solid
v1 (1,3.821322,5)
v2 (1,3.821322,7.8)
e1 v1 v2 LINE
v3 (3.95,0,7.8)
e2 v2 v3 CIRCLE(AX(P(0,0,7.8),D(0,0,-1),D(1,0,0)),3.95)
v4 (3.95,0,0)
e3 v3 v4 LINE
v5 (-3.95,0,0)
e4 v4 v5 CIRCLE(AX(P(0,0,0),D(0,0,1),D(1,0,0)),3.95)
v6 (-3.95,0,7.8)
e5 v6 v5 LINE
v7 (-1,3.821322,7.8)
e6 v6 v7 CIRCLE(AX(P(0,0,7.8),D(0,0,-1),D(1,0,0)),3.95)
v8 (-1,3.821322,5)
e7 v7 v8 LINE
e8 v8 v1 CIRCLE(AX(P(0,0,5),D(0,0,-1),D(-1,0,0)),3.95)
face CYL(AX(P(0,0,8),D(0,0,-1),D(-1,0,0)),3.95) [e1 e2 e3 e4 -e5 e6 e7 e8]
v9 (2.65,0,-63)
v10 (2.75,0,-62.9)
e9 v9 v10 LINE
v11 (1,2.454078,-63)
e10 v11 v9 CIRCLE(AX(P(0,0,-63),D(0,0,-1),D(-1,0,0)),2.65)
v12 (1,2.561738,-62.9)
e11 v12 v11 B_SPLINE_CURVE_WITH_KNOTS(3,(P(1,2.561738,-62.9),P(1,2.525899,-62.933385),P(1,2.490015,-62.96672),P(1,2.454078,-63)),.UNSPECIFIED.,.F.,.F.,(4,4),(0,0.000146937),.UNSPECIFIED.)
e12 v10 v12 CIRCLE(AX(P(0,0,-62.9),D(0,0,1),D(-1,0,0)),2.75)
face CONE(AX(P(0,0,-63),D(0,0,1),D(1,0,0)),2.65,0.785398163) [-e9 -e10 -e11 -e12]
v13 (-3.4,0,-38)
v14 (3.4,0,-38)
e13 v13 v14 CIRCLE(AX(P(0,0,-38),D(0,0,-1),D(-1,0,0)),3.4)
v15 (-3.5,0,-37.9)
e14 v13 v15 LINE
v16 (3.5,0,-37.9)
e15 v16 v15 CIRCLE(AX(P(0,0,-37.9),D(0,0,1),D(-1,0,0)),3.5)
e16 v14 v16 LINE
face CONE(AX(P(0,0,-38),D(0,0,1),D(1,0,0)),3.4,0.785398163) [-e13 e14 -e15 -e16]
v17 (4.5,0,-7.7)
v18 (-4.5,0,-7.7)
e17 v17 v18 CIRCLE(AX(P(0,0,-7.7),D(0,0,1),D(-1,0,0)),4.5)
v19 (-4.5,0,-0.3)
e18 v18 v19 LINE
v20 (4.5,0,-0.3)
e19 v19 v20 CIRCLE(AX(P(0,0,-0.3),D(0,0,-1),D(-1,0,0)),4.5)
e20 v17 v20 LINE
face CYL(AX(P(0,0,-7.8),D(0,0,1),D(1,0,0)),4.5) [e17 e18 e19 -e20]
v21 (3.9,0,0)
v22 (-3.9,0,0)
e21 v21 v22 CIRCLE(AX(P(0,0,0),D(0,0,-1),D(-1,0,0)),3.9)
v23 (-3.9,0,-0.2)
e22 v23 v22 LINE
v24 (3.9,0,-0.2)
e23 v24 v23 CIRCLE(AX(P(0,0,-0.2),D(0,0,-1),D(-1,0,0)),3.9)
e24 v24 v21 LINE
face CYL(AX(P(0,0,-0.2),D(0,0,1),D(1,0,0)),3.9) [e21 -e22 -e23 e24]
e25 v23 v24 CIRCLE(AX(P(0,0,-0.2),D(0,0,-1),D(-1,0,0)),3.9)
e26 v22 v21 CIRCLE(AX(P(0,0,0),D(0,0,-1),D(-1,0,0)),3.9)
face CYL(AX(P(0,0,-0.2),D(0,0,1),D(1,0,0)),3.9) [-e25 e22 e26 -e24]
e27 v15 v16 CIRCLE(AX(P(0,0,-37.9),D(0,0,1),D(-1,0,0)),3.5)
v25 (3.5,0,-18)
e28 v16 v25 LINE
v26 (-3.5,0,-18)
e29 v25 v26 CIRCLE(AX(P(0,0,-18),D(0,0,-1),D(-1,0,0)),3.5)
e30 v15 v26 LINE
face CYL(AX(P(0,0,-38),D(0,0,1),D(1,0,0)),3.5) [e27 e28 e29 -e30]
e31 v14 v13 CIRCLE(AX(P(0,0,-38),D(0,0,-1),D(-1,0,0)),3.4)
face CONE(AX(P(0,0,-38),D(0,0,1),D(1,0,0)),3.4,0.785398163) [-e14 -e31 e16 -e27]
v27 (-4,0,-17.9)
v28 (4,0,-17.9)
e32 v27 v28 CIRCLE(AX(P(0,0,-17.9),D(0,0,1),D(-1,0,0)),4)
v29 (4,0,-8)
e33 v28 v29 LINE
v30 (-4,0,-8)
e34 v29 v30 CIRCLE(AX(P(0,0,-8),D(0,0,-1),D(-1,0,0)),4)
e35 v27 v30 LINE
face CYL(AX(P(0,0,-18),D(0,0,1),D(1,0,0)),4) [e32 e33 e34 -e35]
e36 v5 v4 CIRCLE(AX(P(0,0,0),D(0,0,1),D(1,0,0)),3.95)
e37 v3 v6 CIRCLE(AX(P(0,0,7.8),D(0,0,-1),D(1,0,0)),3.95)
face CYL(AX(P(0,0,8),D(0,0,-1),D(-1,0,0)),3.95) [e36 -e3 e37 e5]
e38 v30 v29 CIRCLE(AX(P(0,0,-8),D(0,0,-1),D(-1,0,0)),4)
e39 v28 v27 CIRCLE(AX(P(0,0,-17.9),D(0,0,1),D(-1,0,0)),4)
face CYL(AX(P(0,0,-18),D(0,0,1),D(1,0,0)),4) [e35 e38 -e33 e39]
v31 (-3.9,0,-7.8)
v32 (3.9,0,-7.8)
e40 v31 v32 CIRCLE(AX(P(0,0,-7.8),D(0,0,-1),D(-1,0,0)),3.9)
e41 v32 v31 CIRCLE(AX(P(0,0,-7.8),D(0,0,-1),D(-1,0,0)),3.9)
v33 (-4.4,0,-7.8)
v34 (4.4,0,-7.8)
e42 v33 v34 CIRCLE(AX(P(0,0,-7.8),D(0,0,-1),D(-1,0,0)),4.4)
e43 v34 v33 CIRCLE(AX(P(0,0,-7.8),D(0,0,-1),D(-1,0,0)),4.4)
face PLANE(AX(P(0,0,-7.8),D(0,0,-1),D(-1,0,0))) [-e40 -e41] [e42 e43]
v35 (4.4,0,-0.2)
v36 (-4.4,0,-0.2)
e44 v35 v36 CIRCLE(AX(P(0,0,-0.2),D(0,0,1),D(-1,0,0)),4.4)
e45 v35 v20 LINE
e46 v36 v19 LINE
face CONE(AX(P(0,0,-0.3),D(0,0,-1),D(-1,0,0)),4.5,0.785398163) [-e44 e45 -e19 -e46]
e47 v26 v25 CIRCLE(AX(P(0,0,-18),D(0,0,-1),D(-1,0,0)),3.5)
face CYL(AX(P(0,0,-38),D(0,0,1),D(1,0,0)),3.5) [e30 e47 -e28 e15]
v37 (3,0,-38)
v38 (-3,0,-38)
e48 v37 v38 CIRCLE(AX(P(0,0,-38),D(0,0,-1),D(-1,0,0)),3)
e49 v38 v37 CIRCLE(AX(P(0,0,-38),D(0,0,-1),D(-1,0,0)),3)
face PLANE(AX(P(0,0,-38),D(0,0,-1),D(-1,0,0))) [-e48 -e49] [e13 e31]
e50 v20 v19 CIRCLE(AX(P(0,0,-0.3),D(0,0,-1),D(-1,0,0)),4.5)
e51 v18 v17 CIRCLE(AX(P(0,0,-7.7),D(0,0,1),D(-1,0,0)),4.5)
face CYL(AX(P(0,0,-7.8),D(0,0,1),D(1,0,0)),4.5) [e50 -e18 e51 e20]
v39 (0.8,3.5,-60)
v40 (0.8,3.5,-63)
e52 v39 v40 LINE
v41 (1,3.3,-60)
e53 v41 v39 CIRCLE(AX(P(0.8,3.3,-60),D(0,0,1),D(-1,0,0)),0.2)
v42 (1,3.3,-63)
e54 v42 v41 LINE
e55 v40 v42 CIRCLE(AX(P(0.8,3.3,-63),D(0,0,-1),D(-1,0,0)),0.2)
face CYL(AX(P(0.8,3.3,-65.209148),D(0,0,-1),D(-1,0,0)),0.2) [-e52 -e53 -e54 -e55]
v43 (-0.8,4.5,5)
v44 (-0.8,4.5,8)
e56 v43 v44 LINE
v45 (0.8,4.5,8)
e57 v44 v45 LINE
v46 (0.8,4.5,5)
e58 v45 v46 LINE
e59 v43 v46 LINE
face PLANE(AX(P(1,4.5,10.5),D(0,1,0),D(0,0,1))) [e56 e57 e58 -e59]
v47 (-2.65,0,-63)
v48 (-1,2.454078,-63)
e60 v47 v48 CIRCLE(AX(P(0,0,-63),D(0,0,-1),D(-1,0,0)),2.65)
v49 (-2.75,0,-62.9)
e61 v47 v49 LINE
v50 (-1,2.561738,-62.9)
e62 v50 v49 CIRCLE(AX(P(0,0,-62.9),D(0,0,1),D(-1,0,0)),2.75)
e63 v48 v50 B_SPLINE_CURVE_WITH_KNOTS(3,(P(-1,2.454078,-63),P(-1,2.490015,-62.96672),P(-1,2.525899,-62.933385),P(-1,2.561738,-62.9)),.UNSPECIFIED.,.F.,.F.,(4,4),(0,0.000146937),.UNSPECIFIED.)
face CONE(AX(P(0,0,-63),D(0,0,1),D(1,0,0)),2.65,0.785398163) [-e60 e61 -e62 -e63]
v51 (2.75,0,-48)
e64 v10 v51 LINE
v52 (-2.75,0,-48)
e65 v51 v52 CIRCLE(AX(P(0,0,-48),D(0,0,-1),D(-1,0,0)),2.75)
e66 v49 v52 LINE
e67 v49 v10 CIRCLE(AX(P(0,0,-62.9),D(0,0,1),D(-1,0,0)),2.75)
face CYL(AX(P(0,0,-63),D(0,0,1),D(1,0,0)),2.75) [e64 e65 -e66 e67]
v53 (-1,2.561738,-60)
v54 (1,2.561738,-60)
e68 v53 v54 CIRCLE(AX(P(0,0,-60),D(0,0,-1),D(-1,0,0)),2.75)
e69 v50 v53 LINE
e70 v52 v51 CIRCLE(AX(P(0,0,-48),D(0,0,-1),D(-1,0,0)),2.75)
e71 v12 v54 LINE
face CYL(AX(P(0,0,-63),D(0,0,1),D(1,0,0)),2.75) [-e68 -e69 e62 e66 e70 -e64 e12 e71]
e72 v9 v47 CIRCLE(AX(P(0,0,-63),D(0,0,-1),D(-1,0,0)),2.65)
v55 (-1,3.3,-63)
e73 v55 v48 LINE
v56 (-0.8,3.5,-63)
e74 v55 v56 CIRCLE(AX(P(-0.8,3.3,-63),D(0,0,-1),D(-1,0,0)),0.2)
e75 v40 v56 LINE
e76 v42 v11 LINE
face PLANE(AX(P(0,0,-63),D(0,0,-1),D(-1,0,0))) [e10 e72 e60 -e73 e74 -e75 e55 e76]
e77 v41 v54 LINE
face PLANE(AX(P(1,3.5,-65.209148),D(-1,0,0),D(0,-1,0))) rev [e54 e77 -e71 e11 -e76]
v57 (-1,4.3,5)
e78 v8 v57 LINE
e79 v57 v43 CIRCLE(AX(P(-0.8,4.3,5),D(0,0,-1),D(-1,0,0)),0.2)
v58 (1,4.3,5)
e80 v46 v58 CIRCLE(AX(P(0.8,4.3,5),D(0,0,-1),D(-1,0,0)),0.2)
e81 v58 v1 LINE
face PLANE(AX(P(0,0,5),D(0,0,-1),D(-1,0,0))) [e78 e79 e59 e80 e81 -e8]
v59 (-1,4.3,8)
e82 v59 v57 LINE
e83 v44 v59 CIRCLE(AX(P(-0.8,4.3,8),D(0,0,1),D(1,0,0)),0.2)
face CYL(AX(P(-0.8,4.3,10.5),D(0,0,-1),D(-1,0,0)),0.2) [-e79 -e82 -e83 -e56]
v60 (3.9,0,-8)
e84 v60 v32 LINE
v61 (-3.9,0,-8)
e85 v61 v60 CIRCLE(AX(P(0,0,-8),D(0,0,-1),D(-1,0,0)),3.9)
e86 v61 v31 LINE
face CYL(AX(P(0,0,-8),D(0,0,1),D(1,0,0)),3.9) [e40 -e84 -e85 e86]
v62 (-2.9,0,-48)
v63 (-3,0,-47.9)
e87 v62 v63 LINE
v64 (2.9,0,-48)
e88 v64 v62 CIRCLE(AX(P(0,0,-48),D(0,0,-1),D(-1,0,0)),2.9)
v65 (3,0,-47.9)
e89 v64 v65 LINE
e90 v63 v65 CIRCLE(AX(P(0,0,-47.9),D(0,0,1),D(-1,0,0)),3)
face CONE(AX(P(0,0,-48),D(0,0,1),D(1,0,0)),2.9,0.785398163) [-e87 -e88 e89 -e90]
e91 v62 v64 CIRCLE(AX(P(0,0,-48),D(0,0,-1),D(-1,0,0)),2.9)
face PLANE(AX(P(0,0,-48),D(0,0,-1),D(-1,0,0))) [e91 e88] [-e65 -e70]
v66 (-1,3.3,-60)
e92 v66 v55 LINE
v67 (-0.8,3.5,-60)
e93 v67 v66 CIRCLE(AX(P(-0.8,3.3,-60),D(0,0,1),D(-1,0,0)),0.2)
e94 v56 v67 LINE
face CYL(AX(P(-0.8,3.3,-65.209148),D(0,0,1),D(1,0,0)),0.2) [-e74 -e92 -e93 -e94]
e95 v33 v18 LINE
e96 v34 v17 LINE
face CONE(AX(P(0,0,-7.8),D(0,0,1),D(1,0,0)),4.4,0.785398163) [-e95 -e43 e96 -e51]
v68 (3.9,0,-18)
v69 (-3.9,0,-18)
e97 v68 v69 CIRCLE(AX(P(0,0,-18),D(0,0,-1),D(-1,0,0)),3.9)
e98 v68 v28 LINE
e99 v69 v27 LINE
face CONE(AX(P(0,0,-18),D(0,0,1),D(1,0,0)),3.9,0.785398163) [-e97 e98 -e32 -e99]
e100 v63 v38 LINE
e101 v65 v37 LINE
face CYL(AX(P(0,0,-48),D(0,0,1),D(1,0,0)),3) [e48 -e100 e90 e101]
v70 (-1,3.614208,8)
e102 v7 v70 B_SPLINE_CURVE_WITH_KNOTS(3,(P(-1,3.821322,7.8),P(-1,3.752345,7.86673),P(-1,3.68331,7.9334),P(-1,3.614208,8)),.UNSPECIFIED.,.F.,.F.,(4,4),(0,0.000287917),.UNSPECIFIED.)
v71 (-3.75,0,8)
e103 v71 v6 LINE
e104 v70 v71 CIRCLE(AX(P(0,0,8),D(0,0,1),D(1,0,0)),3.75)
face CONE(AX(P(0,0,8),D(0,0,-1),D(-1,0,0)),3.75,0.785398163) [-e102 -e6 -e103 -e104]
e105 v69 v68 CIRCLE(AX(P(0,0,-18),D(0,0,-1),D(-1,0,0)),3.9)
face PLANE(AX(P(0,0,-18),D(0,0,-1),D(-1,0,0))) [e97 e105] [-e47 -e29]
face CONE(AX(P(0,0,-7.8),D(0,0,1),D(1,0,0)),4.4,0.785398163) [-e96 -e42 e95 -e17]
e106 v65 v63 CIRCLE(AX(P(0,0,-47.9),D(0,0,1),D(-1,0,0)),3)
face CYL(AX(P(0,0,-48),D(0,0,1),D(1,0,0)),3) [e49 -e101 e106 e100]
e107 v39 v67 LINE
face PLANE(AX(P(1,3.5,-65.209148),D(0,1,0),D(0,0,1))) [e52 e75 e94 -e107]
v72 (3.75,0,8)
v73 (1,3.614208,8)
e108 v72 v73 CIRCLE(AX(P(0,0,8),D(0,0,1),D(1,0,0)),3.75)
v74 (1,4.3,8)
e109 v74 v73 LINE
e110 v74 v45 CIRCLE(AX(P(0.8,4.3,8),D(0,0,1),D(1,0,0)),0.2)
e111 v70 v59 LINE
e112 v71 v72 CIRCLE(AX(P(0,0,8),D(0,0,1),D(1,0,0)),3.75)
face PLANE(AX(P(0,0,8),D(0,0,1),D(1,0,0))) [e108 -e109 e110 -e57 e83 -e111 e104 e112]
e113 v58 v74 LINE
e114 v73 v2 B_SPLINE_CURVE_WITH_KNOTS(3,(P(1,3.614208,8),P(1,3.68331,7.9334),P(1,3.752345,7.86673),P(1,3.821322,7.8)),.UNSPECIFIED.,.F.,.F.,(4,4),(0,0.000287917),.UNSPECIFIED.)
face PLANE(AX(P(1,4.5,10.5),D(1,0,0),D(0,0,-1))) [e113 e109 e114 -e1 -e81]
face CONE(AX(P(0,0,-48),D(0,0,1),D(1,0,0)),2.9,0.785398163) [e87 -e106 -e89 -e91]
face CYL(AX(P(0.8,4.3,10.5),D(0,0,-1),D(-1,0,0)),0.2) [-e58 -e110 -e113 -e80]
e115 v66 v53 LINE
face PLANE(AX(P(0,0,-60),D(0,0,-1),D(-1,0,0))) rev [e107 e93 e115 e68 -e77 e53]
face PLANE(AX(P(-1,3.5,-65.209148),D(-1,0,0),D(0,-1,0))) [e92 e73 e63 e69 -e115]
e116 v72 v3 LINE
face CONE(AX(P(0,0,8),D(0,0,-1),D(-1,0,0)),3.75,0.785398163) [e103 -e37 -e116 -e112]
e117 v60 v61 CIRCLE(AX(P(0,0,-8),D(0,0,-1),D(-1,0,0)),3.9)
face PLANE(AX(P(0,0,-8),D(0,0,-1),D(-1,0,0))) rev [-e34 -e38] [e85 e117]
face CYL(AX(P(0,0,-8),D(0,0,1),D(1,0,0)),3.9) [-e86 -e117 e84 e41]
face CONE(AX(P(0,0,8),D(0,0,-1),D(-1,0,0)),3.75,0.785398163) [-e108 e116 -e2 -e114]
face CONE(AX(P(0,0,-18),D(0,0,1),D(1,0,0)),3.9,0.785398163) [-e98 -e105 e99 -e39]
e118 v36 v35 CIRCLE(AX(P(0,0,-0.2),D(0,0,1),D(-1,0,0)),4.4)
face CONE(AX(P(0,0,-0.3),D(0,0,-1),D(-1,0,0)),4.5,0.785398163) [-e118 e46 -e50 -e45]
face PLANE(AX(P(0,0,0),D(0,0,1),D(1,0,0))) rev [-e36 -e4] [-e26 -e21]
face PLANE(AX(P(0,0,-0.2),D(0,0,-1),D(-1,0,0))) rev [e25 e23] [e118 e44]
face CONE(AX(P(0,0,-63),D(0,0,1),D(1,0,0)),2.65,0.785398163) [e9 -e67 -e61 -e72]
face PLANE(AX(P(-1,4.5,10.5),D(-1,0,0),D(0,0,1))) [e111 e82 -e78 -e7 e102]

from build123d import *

# Parameters (mm, degrees)
SKETCH1_R            = 3.95
BOSS_EXTRUDE1_DEPTH  = 8
SKETCH2_W            = 2
SKETCH2_H            = 1.5
BOSS_EXTRUDE2_DEPTH  = 3
FILLET1_R            = 0.2
SKETCH3_R            = 3.9
BOSS_EXTRUDE3_DEPTH  = 0.2
SKETCH4_R            = 4.5
BOSS_EXTRUDE4_DEPTH  = 7.6
SKETCH6_R            = 3.9
BOSS_EXTRUDE5_DEPTH  = 0.2
CHAMFER2_SIZE        = 0.2
SKETCH7_R            = 4
BOSS_EXTRUDE8_DEPTH  = 10
SKETCH9_R            = 3.5
BOSS_EXTRUDE9_DEPTH  = 20
SKETCH10_R           = 3
BOSS_EXTRUDE10_DEPTH = 10
SKETCH13_R           = 2.75
BOSS_EXTRUDE11_DEPTH = 15
BOSS_EXTRUDE13_DEPTH = 3
FILLET2_R            = 0.2
CHAMFER5_SIZE        = 0.1


with BuildPart() as part:
    # Sketch1 → Boss-Extrude1 (new body)
    with BuildSketch(Plane.XY):
        Circle(SKETCH1_R)
    extrude(amount=BOSS_EXTRUDE1_DEPTH)

    # Sketch2 → Boss-Extrude2 (add)
    with BuildSketch(Plane(origin=(0, 0, 5), x_dir=(-1, 0, 0), z_dir=(0, 0, -1))):
        with Locations((0, 3.75)):
            Rectangle(SKETCH2_W, SKETCH2_H)
    extrude(amount=-BOSS_EXTRUDE2_DEPTH)

    # Fillet1
    fillet1_edges = [part.edges().sort_by_distance(p)[0] for p in [
        (-1, 4.5, 6.5),
        (1, 4.5, 6.5),
    ]]
    fillet(fillet1_edges, radius=FILLET1_R)

    # Sketch3 → Boss-Extrude3 (add)
    with BuildSketch(Plane(origin=(0, 0, 0), x_dir=(-1, 0, 0), z_dir=(0, 0, -1))):
        Circle(SKETCH3_R)
    extrude(amount=BOSS_EXTRUDE3_DEPTH)

    # Sketch4 → Boss-Extrude4 (add)
    with BuildSketch(Plane(origin=(0, 0, -0.2), x_dir=(-1, 0, 0), z_dir=(0, 0, -1))):
        with Locations(Location((0, 0, 0), (0, 0, 180))):
            Circle(SKETCH4_R)
    extrude(amount=BOSS_EXTRUDE4_DEPTH)

    # Sketch6 → Boss-Extrude5 (add)
    with BuildSketch(Plane(origin=(0, 0, -7.8), x_dir=(-1, 0, 0), z_dir=(0, 0, -1))):
        Circle(SKETCH6_R)
    extrude(amount=BOSS_EXTRUDE5_DEPTH)

    # Chamfer2
    chamfer2_edges = [part.edges().sort_by_distance(p)[0] for p in [
        (-2.413762623, -3.126699538, 8),
    ]]
    chamfer(chamfer2_edges, length=CHAMFER2_SIZE)

    # Sketch7 → Boss-Extrude8 (add)
    with BuildSketch(Plane(origin=(0, 0, -8), x_dir=(-1, 0, 0), z_dir=(0, 0, -1))):
        Circle(SKETCH7_R)
    extrude(amount=BOSS_EXTRUDE8_DEPTH)

    # Sketch9 → Boss-Extrude9 (add)
    with BuildSketch(Plane(origin=(0, 0, -18), x_dir=(-1, 0, 0), z_dir=(0, 0, -1))):
        Circle(SKETCH9_R)
    extrude(amount=BOSS_EXTRUDE9_DEPTH)

    # Sketch10 → Boss-Extrude10 (add)
    with BuildSketch(Plane(origin=(0, 0, -38), x_dir=(-1, 0, 0), z_dir=(0, 0, -1))):
        Circle(SKETCH10_R)
    extrude(amount=BOSS_EXTRUDE10_DEPTH)

    # Sketch13 → Boss-Extrude11 (add)
    with BuildSketch(Plane(origin=(0, 0, -48), x_dir=(-1, 0, 0), z_dir=(0, 0, -1))):
        Circle(SKETCH13_R)
    extrude(amount=BOSS_EXTRUDE11_DEPTH)

    # Sketch14 → Boss-Extrude13 (add)
    with BuildSketch(Plane(origin=(0, 0, -60), x_dir=(-1, 0, 0), z_dir=(0, 0, -1))):
        with BuildLine():
            Line((-1, 3.5), (1, 3.5))
            Line((1, 3.5), (1, 2.561737691))
            ThreePointArc((1, 2.561737691), (0, 2.75), (-1, 2.561737691))
            Line((-1, 2.561737691), (-1, 3.5))
        make_face()
    extrude(amount=BOSS_EXTRUDE13_DEPTH)

    # Fillet2
    fillet2_edges = [part.edges().sort_by_distance(p)[0] for p in [
        (-1, 3.5, -61.5),
        (1, 3.5, -61.5),
    ]]
    fillet(fillet2_edges, radius=FILLET2_R)

    # Chamfer5
    chamfer5_edges = [part.edges().sort_by_distance(p)[0] for p in [
        (-4.5, 0, -0.2),
        (-4.5, 0, -7.8),
        (4, 0, -18),
        (3.5, 0, -38),
        (3, 0, -48),
        (1.551209206, -2.270737766, -63),
    ]]
    chamfer(chamfer5_edges, length=CHAMFER5_SIZE)


solid = part.part
